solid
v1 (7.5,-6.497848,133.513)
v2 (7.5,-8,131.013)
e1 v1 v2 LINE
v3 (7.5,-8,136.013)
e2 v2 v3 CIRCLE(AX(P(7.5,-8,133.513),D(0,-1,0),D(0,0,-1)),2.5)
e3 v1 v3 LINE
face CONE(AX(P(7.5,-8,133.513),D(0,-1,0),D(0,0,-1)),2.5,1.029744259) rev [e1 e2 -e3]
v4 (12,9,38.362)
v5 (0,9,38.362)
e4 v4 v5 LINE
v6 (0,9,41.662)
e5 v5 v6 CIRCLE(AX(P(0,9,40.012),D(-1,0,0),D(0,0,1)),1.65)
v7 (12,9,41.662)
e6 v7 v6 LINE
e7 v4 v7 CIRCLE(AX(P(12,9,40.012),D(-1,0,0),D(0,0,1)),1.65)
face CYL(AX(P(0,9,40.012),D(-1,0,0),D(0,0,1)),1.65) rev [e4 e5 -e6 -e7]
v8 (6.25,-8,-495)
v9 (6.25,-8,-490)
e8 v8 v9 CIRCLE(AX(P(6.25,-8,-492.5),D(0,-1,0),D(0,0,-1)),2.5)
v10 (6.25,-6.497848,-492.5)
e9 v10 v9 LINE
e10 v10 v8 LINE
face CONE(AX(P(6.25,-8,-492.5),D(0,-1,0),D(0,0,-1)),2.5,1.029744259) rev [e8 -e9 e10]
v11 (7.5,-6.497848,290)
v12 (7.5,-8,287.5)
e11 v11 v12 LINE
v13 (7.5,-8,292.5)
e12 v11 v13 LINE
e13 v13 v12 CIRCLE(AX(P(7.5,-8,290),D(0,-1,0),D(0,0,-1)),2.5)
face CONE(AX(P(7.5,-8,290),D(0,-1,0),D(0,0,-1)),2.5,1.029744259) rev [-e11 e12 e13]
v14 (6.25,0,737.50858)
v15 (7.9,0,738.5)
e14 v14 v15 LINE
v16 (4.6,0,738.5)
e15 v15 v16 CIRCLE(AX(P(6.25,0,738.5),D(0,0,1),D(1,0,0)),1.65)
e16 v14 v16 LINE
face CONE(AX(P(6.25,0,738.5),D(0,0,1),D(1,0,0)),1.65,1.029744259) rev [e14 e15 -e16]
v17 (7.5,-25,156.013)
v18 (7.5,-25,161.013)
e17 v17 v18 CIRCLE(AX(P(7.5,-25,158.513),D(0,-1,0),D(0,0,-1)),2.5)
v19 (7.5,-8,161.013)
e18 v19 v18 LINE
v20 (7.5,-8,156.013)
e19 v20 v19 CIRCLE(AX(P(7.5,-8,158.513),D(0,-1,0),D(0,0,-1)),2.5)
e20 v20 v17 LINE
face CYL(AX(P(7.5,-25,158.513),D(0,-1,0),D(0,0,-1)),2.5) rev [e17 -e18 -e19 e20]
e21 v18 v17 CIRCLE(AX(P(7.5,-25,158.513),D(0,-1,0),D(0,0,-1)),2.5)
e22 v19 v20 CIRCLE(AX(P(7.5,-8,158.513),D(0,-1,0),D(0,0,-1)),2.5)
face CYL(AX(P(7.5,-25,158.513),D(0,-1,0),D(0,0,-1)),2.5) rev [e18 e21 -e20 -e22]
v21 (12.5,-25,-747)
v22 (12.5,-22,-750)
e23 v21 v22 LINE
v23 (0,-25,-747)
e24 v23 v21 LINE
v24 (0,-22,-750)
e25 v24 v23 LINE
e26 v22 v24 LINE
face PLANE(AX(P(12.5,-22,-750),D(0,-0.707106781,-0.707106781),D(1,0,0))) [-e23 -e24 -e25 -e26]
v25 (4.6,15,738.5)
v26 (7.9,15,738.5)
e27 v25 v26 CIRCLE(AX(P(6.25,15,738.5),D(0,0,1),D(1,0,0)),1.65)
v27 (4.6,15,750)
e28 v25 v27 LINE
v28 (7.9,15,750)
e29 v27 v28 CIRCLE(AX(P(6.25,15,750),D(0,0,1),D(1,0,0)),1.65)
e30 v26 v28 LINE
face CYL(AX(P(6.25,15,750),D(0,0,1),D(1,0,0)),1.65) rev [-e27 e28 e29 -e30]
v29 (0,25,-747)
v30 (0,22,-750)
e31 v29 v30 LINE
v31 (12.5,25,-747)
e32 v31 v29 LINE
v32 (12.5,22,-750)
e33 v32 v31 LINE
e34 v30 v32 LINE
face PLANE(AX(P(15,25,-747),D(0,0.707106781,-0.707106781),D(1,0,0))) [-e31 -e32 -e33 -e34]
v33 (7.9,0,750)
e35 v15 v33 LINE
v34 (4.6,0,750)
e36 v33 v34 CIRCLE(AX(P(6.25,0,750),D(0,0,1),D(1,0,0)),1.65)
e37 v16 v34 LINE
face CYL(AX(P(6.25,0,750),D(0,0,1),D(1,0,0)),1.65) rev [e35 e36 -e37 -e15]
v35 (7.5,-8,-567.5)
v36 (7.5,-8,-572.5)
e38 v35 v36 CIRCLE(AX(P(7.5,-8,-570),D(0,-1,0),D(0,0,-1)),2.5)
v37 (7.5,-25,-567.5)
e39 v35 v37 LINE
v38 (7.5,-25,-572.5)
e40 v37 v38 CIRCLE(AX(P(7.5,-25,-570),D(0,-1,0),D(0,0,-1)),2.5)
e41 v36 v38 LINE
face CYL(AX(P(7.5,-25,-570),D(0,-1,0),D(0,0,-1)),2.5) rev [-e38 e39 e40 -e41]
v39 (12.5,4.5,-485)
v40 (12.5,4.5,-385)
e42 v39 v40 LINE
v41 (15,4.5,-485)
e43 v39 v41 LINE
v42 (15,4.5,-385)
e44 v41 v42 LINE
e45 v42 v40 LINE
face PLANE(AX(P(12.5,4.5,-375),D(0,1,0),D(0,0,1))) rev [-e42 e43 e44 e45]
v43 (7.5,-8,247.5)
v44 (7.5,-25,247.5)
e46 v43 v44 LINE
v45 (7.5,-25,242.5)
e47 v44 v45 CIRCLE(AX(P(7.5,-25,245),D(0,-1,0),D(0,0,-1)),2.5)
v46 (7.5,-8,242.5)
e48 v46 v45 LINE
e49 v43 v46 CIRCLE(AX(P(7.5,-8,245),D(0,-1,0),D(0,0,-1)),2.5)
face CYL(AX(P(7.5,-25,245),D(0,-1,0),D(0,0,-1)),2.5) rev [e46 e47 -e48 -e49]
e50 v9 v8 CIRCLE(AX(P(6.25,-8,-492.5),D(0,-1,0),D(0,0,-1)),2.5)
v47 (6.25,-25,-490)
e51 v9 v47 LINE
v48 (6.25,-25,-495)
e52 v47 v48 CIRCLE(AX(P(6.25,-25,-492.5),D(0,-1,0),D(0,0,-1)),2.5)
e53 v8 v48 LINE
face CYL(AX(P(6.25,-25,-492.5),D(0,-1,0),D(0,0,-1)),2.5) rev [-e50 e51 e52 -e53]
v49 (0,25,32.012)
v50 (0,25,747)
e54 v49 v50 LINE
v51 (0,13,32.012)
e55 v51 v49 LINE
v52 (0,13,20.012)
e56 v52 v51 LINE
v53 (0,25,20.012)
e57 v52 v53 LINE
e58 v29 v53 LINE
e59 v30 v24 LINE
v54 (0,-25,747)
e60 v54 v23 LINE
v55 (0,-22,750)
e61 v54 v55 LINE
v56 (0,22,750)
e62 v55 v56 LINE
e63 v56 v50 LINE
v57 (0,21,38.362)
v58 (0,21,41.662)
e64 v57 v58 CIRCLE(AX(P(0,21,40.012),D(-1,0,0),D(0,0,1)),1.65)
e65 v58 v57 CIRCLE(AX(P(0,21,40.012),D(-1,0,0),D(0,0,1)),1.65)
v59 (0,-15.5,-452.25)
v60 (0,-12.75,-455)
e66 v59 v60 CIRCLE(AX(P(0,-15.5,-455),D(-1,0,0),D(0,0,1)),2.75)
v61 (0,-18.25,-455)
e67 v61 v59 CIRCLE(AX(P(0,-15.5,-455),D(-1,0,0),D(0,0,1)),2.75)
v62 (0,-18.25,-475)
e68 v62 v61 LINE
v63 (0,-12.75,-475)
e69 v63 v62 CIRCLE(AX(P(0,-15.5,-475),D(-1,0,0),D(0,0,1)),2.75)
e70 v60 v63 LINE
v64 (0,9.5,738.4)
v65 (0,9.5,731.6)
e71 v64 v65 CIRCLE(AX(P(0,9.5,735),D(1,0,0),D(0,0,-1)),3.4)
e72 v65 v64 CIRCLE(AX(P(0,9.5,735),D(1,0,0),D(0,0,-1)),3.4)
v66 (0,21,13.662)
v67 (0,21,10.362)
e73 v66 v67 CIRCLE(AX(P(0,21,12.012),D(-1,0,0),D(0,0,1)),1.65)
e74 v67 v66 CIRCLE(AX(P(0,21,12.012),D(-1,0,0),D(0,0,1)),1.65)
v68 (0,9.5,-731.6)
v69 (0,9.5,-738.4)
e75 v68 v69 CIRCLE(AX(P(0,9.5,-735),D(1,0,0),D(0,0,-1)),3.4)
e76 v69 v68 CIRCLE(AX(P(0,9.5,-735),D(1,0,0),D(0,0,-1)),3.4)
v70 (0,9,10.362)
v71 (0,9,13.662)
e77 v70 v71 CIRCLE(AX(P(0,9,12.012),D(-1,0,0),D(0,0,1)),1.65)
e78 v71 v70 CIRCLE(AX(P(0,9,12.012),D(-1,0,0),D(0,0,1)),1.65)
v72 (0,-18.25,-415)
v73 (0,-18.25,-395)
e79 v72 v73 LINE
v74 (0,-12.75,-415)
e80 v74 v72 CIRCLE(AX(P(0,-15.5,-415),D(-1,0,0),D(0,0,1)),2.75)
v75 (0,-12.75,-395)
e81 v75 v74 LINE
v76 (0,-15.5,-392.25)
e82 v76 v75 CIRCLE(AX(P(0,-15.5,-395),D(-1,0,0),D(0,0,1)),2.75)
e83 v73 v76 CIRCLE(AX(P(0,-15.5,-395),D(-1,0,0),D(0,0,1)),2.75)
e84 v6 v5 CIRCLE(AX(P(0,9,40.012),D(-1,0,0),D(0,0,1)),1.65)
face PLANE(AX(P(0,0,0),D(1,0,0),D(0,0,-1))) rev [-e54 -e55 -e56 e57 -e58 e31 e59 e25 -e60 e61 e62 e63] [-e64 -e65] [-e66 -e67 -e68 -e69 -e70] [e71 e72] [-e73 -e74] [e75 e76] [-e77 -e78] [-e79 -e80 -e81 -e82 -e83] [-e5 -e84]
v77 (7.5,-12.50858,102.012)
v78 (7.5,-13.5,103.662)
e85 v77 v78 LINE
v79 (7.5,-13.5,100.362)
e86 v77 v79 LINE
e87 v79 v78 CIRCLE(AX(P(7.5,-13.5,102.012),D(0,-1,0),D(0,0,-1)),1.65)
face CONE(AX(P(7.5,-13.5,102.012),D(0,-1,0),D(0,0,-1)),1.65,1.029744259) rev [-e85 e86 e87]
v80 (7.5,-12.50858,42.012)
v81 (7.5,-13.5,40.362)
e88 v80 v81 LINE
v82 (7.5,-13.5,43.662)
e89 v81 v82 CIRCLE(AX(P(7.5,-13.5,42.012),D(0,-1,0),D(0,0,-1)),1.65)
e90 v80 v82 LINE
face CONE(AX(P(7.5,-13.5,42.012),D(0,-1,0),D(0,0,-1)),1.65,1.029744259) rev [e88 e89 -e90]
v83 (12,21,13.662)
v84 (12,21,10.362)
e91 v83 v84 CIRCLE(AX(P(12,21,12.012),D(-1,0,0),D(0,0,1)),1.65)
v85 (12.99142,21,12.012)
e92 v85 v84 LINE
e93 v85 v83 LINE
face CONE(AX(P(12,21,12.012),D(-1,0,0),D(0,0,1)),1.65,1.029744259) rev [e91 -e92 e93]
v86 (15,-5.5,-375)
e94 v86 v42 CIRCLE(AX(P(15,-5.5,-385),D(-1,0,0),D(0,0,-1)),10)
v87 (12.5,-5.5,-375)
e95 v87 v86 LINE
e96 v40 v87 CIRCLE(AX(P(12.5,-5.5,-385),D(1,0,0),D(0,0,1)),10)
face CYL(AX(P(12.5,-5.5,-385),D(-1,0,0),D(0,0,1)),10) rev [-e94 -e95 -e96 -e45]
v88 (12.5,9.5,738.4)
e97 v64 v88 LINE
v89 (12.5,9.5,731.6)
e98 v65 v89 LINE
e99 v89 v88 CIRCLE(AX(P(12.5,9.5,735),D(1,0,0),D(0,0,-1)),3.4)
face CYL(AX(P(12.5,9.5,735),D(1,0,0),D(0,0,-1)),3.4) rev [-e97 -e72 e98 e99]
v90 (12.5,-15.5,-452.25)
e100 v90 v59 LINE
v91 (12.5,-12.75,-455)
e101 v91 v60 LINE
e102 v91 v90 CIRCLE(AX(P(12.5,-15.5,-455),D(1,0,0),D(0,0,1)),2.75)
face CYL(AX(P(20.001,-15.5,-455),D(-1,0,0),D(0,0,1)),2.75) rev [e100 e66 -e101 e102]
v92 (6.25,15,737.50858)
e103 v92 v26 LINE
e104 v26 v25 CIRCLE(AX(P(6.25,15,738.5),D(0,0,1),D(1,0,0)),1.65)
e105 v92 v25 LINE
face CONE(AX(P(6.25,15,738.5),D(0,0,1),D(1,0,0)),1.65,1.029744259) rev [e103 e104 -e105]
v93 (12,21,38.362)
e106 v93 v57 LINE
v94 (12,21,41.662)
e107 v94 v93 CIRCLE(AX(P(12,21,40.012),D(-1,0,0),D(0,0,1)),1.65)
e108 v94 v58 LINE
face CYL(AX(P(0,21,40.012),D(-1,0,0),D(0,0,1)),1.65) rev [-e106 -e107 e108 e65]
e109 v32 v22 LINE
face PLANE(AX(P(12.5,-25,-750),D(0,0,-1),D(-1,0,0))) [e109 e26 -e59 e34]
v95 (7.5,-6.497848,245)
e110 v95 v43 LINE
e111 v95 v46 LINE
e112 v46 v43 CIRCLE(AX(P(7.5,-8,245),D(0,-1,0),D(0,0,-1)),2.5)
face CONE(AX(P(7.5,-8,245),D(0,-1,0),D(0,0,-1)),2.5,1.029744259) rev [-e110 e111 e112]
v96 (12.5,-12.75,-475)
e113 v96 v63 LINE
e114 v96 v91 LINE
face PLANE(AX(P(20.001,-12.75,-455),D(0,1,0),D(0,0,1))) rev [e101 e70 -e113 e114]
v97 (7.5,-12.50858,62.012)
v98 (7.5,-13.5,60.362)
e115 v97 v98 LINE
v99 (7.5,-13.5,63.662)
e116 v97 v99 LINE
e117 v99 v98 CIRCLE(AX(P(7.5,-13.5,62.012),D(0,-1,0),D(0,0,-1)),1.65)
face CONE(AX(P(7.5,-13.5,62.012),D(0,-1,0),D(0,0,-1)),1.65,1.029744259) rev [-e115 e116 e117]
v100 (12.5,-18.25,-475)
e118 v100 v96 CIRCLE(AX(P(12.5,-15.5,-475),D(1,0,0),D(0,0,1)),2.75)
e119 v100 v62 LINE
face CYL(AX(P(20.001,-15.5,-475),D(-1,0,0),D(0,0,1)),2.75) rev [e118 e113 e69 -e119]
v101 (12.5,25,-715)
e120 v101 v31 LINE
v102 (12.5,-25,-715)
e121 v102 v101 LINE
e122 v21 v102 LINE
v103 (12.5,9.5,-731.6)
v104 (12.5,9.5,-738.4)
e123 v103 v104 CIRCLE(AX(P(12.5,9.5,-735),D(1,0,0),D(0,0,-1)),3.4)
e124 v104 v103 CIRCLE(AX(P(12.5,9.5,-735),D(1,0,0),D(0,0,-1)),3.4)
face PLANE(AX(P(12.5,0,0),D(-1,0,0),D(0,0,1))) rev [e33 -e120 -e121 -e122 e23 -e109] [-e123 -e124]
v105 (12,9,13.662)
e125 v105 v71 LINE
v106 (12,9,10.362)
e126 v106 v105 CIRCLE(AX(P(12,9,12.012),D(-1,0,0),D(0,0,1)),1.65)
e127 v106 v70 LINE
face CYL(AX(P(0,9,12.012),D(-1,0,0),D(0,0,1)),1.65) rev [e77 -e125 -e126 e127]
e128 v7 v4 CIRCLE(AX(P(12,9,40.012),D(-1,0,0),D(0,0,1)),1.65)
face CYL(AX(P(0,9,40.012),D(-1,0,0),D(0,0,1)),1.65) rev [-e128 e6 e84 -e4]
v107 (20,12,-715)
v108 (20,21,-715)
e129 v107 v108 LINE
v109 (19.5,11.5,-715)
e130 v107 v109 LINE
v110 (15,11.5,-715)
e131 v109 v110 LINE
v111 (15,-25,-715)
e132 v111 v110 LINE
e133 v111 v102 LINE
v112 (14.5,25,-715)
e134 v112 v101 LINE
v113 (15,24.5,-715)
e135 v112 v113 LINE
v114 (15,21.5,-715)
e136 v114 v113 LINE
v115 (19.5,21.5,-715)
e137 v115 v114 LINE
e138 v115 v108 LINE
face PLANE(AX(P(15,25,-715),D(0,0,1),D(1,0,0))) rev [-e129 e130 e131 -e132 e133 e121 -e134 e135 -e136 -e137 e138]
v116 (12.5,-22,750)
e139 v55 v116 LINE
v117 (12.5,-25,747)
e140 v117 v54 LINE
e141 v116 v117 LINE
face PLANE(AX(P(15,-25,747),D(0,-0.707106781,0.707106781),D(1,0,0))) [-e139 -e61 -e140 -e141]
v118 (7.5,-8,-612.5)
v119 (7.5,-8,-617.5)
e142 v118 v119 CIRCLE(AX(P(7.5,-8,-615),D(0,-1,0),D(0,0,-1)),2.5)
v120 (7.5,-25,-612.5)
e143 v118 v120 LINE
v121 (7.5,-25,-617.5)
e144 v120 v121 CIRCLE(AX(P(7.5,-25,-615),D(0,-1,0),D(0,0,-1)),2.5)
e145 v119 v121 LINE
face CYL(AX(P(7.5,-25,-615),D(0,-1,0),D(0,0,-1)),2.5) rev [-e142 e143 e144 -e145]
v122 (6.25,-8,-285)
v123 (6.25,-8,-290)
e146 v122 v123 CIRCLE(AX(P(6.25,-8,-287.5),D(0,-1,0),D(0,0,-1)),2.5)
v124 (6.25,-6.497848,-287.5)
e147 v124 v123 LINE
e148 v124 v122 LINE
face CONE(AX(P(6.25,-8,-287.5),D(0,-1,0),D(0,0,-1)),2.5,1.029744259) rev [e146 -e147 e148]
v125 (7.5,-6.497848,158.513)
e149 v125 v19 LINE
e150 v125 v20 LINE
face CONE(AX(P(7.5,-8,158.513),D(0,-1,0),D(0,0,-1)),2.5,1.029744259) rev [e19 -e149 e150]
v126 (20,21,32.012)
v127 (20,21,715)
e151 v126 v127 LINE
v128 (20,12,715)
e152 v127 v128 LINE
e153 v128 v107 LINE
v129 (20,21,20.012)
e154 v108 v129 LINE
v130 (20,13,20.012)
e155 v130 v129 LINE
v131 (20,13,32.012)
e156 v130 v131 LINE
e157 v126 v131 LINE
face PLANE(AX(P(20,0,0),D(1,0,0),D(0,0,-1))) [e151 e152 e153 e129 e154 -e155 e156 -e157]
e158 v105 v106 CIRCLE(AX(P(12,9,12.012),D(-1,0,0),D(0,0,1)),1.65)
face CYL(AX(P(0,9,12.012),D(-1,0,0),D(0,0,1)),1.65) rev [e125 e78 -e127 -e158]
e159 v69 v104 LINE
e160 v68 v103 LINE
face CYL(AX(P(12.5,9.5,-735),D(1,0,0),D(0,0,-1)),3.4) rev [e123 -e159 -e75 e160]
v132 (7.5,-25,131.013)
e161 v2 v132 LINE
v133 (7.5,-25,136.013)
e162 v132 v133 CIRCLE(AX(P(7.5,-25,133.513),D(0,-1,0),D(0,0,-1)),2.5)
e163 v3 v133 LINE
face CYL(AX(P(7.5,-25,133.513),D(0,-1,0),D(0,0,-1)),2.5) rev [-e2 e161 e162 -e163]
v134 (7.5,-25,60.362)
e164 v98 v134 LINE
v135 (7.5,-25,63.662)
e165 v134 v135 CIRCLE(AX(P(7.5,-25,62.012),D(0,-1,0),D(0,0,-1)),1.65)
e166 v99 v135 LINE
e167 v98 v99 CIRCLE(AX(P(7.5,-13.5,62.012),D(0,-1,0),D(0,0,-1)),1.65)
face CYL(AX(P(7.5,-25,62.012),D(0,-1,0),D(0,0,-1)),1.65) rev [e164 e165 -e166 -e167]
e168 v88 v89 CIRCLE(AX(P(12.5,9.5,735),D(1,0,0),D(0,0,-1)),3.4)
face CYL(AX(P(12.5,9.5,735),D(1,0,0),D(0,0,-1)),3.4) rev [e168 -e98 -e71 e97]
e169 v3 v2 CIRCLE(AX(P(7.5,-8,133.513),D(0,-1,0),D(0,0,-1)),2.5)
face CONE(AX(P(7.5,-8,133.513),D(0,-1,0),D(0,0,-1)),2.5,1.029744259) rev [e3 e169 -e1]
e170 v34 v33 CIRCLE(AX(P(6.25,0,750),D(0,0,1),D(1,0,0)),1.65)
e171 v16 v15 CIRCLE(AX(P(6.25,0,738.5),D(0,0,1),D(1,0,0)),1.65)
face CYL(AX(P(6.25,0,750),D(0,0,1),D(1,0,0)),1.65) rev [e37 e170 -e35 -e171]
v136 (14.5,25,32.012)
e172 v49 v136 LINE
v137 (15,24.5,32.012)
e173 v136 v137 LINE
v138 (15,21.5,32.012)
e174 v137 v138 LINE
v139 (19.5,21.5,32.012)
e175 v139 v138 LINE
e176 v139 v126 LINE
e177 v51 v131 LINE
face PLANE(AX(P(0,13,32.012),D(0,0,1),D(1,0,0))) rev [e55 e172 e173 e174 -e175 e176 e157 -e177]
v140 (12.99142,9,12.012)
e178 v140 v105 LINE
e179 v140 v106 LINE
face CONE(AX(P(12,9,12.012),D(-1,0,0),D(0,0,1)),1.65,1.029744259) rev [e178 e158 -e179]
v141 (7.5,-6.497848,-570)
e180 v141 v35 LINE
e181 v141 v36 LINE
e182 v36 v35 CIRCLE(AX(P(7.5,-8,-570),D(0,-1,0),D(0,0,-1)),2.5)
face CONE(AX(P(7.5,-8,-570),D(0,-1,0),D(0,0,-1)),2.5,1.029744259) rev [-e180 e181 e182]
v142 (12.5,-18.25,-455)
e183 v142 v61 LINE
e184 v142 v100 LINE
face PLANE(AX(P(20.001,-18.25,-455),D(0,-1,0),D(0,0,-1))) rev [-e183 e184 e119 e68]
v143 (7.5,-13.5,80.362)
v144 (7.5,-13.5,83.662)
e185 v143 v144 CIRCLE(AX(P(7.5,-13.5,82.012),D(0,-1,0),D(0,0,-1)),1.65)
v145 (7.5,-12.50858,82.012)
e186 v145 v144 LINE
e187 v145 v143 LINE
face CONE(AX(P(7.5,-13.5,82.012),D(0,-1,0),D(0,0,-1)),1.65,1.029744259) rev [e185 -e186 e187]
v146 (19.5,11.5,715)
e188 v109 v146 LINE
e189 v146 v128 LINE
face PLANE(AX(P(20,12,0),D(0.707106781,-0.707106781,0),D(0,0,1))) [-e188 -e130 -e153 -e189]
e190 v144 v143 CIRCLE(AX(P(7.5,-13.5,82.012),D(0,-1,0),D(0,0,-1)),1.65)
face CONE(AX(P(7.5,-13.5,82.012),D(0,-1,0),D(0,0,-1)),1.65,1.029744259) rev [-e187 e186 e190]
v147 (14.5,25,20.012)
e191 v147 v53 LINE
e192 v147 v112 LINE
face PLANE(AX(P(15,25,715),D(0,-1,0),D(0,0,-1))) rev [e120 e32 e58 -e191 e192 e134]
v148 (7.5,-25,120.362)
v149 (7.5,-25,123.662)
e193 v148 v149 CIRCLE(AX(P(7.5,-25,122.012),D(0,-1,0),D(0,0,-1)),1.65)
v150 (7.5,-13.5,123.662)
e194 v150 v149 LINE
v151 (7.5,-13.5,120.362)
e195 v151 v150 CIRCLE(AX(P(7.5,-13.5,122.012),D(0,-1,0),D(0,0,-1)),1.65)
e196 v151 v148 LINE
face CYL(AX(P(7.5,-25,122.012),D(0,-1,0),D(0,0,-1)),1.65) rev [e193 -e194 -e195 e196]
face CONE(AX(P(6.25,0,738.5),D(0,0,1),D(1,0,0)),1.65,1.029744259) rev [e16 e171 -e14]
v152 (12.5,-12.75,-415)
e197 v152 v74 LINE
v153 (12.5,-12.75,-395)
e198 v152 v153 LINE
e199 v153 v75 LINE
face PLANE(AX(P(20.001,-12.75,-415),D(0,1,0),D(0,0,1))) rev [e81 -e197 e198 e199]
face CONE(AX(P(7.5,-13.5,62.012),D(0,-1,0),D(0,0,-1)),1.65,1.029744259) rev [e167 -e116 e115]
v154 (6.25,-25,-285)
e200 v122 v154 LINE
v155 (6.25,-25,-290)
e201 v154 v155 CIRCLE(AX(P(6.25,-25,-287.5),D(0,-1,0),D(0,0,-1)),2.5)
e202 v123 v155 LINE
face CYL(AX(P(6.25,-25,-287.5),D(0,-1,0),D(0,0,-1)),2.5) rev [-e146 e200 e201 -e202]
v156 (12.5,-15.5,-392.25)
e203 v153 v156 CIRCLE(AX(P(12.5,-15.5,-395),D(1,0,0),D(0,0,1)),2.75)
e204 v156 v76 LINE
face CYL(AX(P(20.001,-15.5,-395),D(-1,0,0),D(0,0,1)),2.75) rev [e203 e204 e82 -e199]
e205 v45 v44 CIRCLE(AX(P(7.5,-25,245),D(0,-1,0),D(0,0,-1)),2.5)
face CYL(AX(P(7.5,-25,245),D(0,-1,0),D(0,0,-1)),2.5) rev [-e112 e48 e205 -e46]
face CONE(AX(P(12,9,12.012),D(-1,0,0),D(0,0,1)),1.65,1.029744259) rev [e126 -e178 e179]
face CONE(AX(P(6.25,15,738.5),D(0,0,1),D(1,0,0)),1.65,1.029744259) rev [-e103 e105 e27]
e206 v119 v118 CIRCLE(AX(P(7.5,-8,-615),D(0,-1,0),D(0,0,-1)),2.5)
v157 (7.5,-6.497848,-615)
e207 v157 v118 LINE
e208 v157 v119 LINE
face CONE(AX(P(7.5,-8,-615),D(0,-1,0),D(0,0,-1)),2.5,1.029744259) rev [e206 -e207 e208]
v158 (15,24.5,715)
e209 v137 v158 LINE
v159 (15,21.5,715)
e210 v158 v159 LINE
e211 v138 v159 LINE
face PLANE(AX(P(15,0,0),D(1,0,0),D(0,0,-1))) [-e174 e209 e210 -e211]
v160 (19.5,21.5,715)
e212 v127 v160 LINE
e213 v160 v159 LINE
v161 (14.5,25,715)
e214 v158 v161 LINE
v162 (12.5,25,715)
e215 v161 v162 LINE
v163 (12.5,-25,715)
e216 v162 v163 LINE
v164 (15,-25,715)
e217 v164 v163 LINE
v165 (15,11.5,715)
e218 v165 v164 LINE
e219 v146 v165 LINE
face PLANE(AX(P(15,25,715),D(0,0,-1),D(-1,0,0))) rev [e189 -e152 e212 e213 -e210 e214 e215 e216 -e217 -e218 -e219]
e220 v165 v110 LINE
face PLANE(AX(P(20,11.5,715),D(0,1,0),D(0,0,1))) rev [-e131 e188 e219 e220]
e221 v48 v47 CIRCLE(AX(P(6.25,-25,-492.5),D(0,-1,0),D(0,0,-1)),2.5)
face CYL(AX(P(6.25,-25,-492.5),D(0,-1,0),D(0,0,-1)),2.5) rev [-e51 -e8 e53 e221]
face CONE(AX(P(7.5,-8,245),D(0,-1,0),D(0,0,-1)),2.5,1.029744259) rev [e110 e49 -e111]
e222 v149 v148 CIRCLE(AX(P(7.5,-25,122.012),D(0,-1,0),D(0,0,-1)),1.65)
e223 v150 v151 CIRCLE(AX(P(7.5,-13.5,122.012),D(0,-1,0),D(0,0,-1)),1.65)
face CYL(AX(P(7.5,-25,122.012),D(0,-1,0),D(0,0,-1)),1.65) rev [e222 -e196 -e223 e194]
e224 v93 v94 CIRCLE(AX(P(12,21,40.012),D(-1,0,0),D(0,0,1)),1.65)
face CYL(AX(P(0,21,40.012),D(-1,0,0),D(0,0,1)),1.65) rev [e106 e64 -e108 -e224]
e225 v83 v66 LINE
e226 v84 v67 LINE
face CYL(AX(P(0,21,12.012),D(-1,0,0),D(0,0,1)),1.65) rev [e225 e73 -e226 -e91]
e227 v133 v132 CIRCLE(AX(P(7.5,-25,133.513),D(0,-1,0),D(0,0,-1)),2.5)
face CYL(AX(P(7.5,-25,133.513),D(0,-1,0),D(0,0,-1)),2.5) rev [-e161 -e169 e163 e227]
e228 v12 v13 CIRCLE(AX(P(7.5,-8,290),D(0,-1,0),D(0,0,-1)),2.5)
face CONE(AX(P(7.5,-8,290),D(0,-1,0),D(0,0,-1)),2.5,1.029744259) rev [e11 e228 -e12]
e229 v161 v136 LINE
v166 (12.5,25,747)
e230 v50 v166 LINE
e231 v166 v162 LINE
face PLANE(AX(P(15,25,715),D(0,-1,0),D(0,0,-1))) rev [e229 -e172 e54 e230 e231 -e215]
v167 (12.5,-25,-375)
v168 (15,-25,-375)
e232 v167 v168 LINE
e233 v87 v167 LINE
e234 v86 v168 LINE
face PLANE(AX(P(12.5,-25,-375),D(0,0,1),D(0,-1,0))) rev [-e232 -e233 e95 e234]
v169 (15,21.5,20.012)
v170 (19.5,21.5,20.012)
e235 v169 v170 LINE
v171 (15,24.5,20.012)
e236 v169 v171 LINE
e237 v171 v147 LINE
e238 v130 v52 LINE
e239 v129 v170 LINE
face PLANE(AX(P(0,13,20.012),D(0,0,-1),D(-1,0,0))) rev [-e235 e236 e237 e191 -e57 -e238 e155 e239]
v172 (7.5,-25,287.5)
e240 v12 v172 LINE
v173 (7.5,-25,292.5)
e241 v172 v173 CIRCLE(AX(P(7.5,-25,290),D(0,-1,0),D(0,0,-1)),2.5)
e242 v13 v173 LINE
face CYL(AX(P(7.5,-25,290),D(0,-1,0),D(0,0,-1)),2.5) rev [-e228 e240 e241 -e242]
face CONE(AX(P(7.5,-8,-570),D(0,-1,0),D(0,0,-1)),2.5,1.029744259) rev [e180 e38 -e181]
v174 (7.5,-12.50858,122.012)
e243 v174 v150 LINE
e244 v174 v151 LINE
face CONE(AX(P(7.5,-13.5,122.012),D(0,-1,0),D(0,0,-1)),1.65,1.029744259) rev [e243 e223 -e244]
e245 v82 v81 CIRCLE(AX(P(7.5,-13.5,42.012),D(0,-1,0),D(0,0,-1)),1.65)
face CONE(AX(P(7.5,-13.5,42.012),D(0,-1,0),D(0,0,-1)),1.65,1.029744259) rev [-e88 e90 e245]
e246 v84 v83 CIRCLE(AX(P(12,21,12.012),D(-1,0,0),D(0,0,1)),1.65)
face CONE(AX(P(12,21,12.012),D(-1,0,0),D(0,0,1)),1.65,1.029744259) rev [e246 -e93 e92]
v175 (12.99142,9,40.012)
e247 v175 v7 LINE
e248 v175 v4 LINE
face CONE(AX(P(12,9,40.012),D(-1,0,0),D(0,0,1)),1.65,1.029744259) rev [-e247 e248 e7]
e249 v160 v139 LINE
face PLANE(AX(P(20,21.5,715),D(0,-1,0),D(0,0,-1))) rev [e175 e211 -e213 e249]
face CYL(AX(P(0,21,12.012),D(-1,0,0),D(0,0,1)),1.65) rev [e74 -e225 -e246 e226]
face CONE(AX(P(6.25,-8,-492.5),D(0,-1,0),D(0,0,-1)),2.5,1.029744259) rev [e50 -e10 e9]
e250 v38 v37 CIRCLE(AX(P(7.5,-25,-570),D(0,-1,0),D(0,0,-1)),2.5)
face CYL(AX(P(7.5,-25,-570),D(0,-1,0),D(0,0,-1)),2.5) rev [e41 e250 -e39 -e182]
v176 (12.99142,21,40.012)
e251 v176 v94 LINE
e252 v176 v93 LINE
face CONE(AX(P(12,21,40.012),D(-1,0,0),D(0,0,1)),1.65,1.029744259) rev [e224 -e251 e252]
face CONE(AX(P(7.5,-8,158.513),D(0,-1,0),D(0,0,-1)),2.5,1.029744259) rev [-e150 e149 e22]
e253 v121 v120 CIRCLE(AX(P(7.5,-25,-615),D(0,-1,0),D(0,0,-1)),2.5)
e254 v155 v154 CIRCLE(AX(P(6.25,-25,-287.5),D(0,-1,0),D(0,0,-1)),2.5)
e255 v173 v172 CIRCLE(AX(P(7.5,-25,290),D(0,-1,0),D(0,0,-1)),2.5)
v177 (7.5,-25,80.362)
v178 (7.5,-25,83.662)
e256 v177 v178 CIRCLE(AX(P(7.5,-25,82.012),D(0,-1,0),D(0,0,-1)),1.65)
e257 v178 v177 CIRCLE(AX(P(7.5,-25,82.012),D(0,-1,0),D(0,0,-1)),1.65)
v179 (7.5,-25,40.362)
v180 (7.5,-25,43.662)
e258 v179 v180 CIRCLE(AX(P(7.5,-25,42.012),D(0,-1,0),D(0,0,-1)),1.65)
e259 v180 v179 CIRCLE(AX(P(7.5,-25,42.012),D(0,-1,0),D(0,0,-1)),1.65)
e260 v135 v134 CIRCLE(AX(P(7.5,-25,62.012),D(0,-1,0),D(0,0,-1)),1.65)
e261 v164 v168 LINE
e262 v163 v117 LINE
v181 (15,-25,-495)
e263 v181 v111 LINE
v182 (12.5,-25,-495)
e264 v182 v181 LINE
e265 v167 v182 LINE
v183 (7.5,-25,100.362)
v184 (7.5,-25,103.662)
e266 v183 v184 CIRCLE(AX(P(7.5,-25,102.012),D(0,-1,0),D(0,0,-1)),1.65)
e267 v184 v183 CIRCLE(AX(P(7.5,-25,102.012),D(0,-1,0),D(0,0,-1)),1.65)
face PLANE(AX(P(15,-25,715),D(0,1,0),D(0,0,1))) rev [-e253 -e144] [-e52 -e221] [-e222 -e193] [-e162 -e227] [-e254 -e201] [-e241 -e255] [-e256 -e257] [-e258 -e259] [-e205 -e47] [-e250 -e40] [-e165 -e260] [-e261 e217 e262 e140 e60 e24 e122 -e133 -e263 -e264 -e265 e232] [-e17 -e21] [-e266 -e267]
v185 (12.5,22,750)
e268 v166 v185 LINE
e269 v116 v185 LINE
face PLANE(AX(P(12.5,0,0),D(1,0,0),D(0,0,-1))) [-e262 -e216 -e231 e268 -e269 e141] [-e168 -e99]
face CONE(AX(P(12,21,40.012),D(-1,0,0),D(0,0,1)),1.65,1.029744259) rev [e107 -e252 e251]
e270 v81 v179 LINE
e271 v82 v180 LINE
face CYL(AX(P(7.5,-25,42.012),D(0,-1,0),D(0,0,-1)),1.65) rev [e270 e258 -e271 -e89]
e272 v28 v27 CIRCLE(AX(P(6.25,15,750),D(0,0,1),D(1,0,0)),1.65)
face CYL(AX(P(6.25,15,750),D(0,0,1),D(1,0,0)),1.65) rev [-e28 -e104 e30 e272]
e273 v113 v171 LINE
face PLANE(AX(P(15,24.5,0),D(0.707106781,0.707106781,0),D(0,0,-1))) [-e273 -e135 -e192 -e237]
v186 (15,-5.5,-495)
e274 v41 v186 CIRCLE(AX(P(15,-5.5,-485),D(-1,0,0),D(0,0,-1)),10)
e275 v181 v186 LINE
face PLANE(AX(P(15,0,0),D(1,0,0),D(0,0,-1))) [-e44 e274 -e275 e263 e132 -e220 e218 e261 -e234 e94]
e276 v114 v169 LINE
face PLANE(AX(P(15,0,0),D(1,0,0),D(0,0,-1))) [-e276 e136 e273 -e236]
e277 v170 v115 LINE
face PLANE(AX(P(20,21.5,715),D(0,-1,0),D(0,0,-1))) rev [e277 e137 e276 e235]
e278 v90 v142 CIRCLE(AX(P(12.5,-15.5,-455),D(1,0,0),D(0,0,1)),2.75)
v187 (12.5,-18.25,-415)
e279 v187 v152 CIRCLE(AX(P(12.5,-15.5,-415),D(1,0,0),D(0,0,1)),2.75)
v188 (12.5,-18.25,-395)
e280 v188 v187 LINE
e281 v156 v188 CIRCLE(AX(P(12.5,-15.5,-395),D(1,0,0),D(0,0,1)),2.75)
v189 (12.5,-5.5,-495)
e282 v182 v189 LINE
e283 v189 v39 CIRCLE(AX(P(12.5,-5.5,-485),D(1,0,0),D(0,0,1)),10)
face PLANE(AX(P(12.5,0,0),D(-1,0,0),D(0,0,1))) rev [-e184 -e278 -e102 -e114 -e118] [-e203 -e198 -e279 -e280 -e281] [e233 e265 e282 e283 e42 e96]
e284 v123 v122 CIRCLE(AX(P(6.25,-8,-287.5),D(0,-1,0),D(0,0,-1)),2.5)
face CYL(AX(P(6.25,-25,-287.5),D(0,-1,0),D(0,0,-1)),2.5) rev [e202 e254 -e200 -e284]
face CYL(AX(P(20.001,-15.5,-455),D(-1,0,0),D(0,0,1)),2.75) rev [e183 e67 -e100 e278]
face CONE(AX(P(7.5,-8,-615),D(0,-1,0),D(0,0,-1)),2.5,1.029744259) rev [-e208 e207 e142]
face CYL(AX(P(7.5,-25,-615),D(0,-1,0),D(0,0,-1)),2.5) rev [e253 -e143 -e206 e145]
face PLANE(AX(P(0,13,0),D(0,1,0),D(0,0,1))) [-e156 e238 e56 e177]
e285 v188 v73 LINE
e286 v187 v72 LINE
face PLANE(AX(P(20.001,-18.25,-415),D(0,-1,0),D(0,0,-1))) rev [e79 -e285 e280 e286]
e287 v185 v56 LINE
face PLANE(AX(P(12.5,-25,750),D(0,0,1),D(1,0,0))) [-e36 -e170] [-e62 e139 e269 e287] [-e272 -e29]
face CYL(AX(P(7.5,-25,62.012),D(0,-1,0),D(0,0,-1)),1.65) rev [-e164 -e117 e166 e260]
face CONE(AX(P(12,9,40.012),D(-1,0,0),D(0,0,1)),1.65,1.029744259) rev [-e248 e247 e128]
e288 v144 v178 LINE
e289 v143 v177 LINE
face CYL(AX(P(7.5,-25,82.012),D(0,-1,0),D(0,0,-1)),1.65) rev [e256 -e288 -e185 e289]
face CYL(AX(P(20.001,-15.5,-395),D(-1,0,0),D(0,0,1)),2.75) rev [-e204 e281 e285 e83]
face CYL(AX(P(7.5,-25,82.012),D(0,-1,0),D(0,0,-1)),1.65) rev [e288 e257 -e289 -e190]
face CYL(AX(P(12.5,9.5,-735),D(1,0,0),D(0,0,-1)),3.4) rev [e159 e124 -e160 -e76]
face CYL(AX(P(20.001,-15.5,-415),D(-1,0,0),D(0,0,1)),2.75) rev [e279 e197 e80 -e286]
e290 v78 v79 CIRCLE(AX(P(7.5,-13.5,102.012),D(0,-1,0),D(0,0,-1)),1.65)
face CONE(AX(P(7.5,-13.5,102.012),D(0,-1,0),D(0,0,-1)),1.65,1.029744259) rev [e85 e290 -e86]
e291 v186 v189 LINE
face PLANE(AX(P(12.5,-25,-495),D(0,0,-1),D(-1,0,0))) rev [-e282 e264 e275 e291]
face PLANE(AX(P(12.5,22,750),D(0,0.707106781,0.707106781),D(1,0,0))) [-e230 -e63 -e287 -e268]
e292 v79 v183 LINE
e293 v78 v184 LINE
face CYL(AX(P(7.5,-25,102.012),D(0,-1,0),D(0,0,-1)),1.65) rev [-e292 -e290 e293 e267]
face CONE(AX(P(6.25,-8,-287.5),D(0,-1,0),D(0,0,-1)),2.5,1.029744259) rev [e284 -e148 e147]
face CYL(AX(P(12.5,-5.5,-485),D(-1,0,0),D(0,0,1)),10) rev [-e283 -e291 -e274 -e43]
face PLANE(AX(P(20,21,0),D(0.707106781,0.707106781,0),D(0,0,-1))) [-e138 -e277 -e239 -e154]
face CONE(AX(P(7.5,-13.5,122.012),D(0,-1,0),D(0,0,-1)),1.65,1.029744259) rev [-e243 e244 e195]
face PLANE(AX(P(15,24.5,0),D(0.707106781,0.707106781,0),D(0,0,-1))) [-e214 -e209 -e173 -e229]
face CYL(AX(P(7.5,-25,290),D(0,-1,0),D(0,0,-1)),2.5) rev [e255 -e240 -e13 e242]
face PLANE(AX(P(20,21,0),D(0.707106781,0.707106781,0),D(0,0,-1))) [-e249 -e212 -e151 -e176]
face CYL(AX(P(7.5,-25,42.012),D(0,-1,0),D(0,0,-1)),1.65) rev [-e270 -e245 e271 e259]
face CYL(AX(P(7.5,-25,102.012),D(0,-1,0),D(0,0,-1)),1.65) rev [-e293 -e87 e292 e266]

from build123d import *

# Parameters (mm, degrees)
SKETCH_1_W             = 1430
SKETCH_1_H             = 50
EXTRUDE_1_DEPTH        = 15
SKETCH_5_W             = 1430
SKETCH_5_H             = 10
EXTRUDE_3_DEPTH        = 5
HOLE_WIZARD_M6_1_D     = 5
HOLE_WIZARD_M6_1_DEPTH = 17
HOLE_WIZARD_M6_1_TIP   = 1.502151548
CHAMFER_3_SIZE         = 0.5
SKETCH_11_W            = 35
SKETCH_11_H            = 50
EXTRUDE_4_DEPTH        = 12.5
HOLE_WIZARD_M8_1_D     = 6.8
CHAMFER_4_SIZE         = 3
SKETCH_14_W            = 120
SKETCH_14_H            = 29.5
CUT_EXTRUDE_1_DEPTH    = 2.5
CUT_EXTRUDE_2_REACH    = 752.683
FILLET_1_R             = 10
SKETCH_16_W            = 25.507597837
SKETCH_16_H            = 12
CUT_EXTRUDE_3_DEPTH    = 12
HOLE_WIZARD_M6_2_D     = 5
HOLE_WIZARD_M6_2_DEPTH = 17
HOLE_WIZARD_M6_2_TIP   = 1.502151548
HOLE_WIZARD_M4_1_D     = 3.3
HOLE_WIZARD_M4_1_DEPTH = 12
HOLE_WIZARD_M4_1_TIP   = 0.991420021
HOLE_WIZARD_M6_3_D     = 5
HOLE_WIZARD_M6_3_DEPTH = 17
HOLE_WIZARD_M6_3_TIP   = 1.502151548
HOLE_WIZARD_M4_2_D     = 3.3
HOLE_WIZARD_M4_2_DEPTH = 11.5
HOLE_WIZARD_M4_2_TIP   = 0.991420021
HOLE_WIZARD_M4_3_D     = 3.3
HOLE_WIZARD_M4_3_DEPTH = 11.5
HOLE_WIZARD_M4_3_TIP   = 0.991420021


with BuildPart() as part:
    # 草图1 → 凸台-拉伸1 (new body)
    with BuildSketch(Plane(origin=(0, 0, 0), x_dir=(0, 0, -1), z_dir=(1, 0, 0))):
        Rectangle(SKETCH_1_W, SKETCH_1_H)
    extrude(amount=EXTRUDE_1_DEPTH)

    # 草图5 → 凸台-拉伸3 (add)
    with BuildSketch(Plane(origin=(15, 0, 0), x_dir=(0, 0, -1), z_dir=(1, 0, 0))):
        with Locations((0, 16.5)):
            Rectangle(SKETCH_5_W, SKETCH_5_H)
    extrude(amount=EXTRUDE_3_DEPTH)

    # M6 螺纹孔1
    with Locations(Plane(origin=(-8.30723521, -25, 23.598187195), x_dir=(0, 0, -1), z_dir=(0, -1, 0))):
        with Locations((638.598187195, 15.80723521), (593.598187195, 15.80723521), (-266.401812805, 15.80723521), (-221.401812805, 15.80723521)):
            Hole(HOLE_WIZARD_M6_1_D / 2, depth=HOLE_WIZARD_M6_1_DEPTH)
            with Locations((0, 0, -(HOLE_WIZARD_M6_1_DEPTH + HOLE_WIZARD_M6_1_TIP / 2))):  # 118° drill point
                Cone(0, HOLE_WIZARD_M6_1_D / 2, HOLE_WIZARD_M6_1_TIP, mode=Mode.SUBTRACT)

    # 倒角3
    chamfer_3_edges = [part.edges().sort_by_distance(p)[0] for p in [
        (15, 25, 0),
        (20, 21.5, 0),
        (20, 11.5, 0),
    ]]
    chamfer(chamfer_3_edges, length=CHAMFER_3_SIZE)

    # 草图11 → 凸台-拉伸4 (add)
    with BuildSketch(Plane.ZY):
        with Locations((-732.5, 0)):
            Rectangle(SKETCH_11_W, SKETCH_11_H)
        with Locations((732.5, 0)):
            Rectangle(SKETCH_11_W, SKETCH_11_H)
    extrude(amount=-EXTRUDE_4_DEPTH)

    # M8 螺纹孔1 (through all)
    with Locations(Plane(origin=(12.5, 0, 0), x_dir=(0, 0, -1), z_dir=(1, 0, 0))):
        with Locations((735, 9.5), (-735, 9.5)):
            Hole(HOLE_WIZARD_M8_1_D / 2)

    # 倒角4
    chamfer_4_edges = [part.edges().sort_by_distance(p)[0] for p in [
        (6.25, -25, -750),
        (6.25, 25, -750),
        (6.25, -25, 750),
        (6.25, 25, 750),
    ]]
    chamfer(chamfer_4_edges, length=CHAMFER_4_SIZE)

    # 草图14 → 切除-拉伸1 (cut)
    with BuildSketch(Plane(origin=(15, 0, 0), x_dir=(0, 0, -1), z_dir=(1, 0, 0))):
        with Locations((435, -10.25)):
            Rectangle(SKETCH_14_W, SKETCH_14_H)
    extrude(amount=-CUT_EXTRUDE_1_DEPTH, mode=Mode.SUBTRACT)

    # 草图15 → 切除-拉伸2 (cut, up to next)
    with BuildSketch(Plane.ZY, mode=Mode.PRIVATE) as cut_extrude_2_sk1:
        with BuildLine():
            Line((-415, -12.75), (-395, -12.75))
            ThreePointArc((-395, -12.75), (-392.25, -15.5), (-395, -18.25))
            Line((-395, -18.25), (-415, -18.25))
            ThreePointArc((-415, -18.25), (-417.75, -15.5), (-415, -12.75))
        make_face()
    cut_extrude_2_tool1 = extrude(cut_extrude_2_sk1.sketch, amount=-CUT_EXTRUDE_2_REACH, mode=Mode.PRIVATE) & part.part
    # 草图15 → 切除-拉伸2 (cut, up to next)
    with BuildSketch(Plane.ZY, mode=Mode.PRIVATE) as cut_extrude_2_sk2:
        with BuildLine():
            Line((-455, -18.25), (-475, -18.25))
            ThreePointArc((-475, -18.25), (-477.75, -15.5), (-475, -12.75))
            Line((-475, -12.75), (-455, -12.75))
            ThreePointArc((-455, -12.75), (-452.25, -15.5), (-455, -18.25))
        make_face()
    cut_extrude_2_tool2 = extrude(cut_extrude_2_sk2.sketch, amount=-CUT_EXTRUDE_2_REACH, mode=Mode.PRIVATE) & part.part
    add(cut_extrude_2_tool1.solids().sort_by_distance((0, -15.5, -405))[0], mode=Mode.SUBTRACT)
    add(cut_extrude_2_tool2.solids().sort_by_distance((0, -15.5, -465))[0], mode=Mode.SUBTRACT)

    # 圆角1
    fillet_1_edges = [part.edges().sort_by_distance(p)[0] for p in [
        (13.75, 4.5, -375),
        (13.75, 4.5, -495),
    ]]
    fillet(fillet_1_edges, radius=FILLET_1_R)

    # 草图16 → 切除-拉伸3 (cut)
    with BuildSketch(Plane(origin=(0, 25, 0), x_dir=(1, 0, 0), z_dir=(0, 1, 0))):
        with Locations((12.753798919, -26.012)):
            Rectangle(SKETCH_16_W, SKETCH_16_H)
    extrude(amount=-CUT_EXTRUDE_3_DEPTH, mode=Mode.SUBTRACT)

    # M6 螺纹孔2
    with Locations(Plane(origin=(0, -25, 0), x_dir=(-1, 0, 0), z_dir=(0, -1, 0))):
        with Locations((-7.5, -133.513), (-7.5, -158.513)):
            Hole(HOLE_WIZARD_M6_2_D / 2, depth=HOLE_WIZARD_M6_2_DEPTH)
            with Locations((0, 0, -(HOLE_WIZARD_M6_2_DEPTH + HOLE_WIZARD_M6_2_TIP / 2))):  # 118° drill point
                Cone(0, HOLE_WIZARD_M6_2_D / 2, HOLE_WIZARD_M6_2_TIP, mode=Mode.SUBTRACT)

    # M4 螺纹孔1
    with Locations(Plane.ZY):
        with Locations((12.012, 21), (12.012, 9), (40.012, 21), (40.012, 9)):
            Hole(HOLE_WIZARD_M4_1_D / 2, depth=HOLE_WIZARD_M4_1_DEPTH)
            with Locations((0, 0, -(HOLE_WIZARD_M4_1_DEPTH + HOLE_WIZARD_M4_1_TIP / 2))):  # 118° drill point
                Cone(0, HOLE_WIZARD_M4_1_D / 2, HOLE_WIZARD_M4_1_TIP, mode=Mode.SUBTRACT)

    # M6 螺纹孔3
    with Locations(Plane(origin=(0, -25, 0), x_dir=(-1, 0, 0), z_dir=(0, -1, 0))):
        with Locations((-6.25, 287.5), (-6.25, 492.5)):
            Hole(HOLE_WIZARD_M6_3_D / 2, depth=HOLE_WIZARD_M6_3_DEPTH)
            with Locations((0, 0, -(HOLE_WIZARD_M6_3_DEPTH + HOLE_WIZARD_M6_3_TIP / 2))):  # 118° drill point
                Cone(0, HOLE_WIZARD_M6_3_D / 2, HOLE_WIZARD_M6_3_TIP, mode=Mode.SUBTRACT)

    # M4 螺纹孔2
    with Locations(Plane.XY.offset(750)):
        with Locations((6.25, 15), (6.25, 0)):
            Hole(HOLE_WIZARD_M4_2_D / 2, depth=HOLE_WIZARD_M4_2_DEPTH)
            with Locations((0, 0, -(HOLE_WIZARD_M4_2_DEPTH + HOLE_WIZARD_M4_2_TIP / 2))):  # 118° drill point
                Cone(0, HOLE_WIZARD_M4_2_D / 2, HOLE_WIZARD_M4_2_TIP, mode=Mode.SUBTRACT)

    # M4 螺纹孔3
    with Locations(Plane(origin=(0, -25, 0), x_dir=(-1, 0, 0), z_dir=(0, -1, 0))):
        with Locations((-7.5, -42.012), (-7.5, -62.012), (-7.5, -82.012), (-7.5, -102.012), (-7.5, -122.012)):
            Hole(HOLE_WIZARD_M4_3_D / 2, depth=HOLE_WIZARD_M4_3_DEPTH)
            with Locations((0, 0, -(HOLE_WIZARD_M4_3_DEPTH + HOLE_WIZARD_M4_3_TIP / 2))):  # 118° drill point
                Cone(0, HOLE_WIZARD_M4_3_D / 2, HOLE_WIZARD_M4_3_TIP, mode=Mode.SUBTRACT)


solid = part.part
